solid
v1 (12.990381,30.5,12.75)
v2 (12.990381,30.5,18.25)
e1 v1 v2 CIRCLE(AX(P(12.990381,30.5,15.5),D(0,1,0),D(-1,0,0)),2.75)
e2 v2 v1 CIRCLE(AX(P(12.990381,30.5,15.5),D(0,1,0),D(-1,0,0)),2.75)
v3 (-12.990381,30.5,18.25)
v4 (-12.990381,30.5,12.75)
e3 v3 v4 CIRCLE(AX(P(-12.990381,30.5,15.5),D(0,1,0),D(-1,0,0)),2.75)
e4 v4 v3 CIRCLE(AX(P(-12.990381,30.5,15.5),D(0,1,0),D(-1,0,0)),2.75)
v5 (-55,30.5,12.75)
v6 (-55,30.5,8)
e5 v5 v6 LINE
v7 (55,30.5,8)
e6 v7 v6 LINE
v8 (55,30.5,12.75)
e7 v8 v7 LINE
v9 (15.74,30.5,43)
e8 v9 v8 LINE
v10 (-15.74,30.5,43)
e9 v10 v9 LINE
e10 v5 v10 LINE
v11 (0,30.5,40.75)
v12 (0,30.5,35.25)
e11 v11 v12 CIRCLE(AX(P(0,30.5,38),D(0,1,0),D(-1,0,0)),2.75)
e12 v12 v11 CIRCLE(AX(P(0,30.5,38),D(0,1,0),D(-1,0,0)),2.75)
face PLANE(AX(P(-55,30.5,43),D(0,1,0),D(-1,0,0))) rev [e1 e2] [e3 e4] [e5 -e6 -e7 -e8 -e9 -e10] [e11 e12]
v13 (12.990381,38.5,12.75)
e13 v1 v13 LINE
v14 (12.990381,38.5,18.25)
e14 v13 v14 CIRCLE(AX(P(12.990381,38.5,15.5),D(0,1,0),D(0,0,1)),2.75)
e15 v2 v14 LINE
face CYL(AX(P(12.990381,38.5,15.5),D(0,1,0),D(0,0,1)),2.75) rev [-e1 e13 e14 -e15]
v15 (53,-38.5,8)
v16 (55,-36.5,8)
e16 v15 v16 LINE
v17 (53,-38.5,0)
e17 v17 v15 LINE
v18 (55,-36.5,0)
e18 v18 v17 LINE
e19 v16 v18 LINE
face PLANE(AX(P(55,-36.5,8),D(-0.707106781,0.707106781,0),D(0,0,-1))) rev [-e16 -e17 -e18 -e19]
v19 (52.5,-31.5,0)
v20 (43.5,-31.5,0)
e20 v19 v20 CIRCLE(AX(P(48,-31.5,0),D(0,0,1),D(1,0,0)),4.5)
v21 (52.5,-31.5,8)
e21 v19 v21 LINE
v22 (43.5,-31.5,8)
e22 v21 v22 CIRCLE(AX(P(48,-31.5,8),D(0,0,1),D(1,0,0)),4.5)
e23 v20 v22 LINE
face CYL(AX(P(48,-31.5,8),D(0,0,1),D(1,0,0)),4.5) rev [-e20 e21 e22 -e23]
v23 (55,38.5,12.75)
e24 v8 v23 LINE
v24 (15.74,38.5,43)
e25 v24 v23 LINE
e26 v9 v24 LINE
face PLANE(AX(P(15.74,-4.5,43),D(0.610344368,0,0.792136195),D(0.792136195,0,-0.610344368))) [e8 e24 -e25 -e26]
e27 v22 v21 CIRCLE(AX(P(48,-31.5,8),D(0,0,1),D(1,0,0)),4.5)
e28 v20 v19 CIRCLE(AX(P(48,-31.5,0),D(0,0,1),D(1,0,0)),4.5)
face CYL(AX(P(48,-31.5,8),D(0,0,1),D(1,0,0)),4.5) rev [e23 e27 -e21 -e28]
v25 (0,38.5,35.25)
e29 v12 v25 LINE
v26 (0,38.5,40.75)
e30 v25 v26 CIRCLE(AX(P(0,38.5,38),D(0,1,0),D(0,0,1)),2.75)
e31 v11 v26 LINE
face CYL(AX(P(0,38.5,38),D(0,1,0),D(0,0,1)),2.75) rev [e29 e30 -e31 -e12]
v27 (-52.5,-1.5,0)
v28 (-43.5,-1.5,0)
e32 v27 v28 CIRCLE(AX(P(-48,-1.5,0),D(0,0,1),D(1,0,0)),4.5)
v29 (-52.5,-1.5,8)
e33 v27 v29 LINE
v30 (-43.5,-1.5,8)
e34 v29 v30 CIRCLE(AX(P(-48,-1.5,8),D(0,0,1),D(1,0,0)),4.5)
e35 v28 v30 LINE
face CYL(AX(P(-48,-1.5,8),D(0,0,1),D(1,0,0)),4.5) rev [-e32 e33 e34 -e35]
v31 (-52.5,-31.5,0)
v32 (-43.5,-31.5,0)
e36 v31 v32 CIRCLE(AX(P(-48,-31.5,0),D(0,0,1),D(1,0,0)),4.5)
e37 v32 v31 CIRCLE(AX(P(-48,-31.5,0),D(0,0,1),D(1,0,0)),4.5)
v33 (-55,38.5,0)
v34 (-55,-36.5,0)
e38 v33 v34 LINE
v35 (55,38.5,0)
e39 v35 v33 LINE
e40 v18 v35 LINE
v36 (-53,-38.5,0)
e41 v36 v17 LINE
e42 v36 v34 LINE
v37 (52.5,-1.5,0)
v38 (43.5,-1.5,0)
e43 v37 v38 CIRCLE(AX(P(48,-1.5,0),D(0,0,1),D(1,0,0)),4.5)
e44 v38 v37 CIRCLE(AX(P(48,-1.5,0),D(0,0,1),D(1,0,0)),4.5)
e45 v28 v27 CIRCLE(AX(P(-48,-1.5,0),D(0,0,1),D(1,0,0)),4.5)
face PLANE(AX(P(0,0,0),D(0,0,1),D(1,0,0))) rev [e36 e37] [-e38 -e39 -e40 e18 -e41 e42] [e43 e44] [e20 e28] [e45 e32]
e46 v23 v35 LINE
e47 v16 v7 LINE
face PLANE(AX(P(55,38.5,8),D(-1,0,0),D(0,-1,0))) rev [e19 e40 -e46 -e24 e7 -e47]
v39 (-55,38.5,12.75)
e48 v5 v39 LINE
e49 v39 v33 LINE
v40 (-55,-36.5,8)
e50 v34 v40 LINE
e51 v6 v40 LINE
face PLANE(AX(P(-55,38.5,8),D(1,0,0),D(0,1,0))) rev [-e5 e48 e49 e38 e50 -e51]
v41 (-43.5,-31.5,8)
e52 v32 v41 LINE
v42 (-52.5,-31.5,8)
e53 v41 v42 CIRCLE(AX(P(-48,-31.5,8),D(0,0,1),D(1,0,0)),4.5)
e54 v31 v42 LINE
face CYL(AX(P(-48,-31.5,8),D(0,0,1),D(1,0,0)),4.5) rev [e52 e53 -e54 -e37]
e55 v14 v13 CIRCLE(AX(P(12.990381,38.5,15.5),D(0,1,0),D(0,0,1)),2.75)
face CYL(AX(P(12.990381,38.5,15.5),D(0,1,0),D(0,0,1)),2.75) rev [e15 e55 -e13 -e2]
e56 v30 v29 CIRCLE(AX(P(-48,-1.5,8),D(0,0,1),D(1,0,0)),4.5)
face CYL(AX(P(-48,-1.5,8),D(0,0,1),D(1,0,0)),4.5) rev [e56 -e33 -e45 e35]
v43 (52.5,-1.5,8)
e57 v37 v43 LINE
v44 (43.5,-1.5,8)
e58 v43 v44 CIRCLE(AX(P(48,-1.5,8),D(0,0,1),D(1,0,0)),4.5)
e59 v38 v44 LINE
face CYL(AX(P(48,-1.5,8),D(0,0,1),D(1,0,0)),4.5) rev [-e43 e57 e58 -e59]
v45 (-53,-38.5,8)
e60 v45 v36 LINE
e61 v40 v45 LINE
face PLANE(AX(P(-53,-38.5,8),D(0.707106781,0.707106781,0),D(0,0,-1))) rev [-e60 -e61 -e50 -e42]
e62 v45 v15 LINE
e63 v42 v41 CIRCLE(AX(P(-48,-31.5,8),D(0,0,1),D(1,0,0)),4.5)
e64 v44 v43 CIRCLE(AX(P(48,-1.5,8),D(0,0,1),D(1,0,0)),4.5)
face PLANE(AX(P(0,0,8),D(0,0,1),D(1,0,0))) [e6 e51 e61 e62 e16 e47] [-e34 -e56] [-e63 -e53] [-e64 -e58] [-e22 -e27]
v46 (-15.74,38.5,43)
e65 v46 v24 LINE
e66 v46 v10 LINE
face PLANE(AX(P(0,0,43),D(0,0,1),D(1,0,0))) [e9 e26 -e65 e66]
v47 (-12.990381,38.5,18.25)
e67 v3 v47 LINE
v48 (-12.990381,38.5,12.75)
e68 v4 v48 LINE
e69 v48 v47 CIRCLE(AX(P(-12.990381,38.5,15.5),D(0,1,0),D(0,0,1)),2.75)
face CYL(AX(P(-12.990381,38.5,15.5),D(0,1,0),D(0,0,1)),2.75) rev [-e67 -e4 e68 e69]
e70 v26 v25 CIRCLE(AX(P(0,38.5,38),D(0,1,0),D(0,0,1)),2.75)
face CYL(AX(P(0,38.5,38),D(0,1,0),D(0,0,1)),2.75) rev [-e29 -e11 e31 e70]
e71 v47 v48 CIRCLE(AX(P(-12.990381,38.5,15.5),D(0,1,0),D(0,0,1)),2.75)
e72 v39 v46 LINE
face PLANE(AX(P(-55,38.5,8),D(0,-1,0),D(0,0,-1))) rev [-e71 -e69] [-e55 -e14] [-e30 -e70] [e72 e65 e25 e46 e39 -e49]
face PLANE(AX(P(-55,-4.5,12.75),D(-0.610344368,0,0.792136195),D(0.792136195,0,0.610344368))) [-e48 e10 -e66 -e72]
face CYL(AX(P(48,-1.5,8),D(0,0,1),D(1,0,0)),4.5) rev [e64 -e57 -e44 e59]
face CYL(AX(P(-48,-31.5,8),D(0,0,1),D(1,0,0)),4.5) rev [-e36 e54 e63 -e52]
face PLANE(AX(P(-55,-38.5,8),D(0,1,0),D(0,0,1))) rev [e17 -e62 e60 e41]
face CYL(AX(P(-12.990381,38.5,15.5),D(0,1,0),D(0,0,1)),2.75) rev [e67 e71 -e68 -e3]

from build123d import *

# Parameters (mm, degrees)
SKETCH_1_W              = 110
SKETCH_1_H              = 77
EXTRUDE_1_DEPTH         = 8
SKETCH_2_W              = 110
SKETCH_2_H              = 8
EXTRUDE_3_DEPTH         = 43
SKETCH_4_OUTSIDE_W      = 140.198
SKETCH_4_OUTSIDE_H      = 73.198
CUT_EXTRUDE_1_DEPTH     = 43
HOLE_WIZARD_7_0_7_1_D   = 9
HOLE_WIZARD_5_5_5_5_2_D = 5.5
CHAMFER_1_SIZE          = 2


with BuildPart() as part:
    # 草图1 → 凸台-拉伸1 (new body)
    with BuildSketch(Plane.XY):
        Rectangle(SKETCH_1_W, SKETCH_1_H)
    extrude(amount=EXTRUDE_1_DEPTH)

    # 草图2 → 凸台-拉伸3 (add)
    with BuildSketch(Plane.XY):
        with Locations((0, 34.5)):
            Rectangle(SKETCH_2_W, SKETCH_2_H)
    extrude(amount=EXTRUDE_3_DEPTH)

    # 草图4 outside → 切除-拉伸1 (cut)
    with BuildSketch(Plane(origin=(0, 38.5, 0), x_dir=(1, 0, 0), z_dir=(0, 1, 0))):
        with Locations((0, -21.5)):
            Rectangle(SKETCH_4_OUTSIDE_W, SKETCH_4_OUTSIDE_H)
        Polygon((-55, 0), (55, 0), (55, -12.75), (15.74, -43), (-15.74, -43), (-55, -12.75), align=None, mode=Mode.SUBTRACT)
    extrude(amount=-CUT_EXTRUDE_1_DEPTH, mode=Mode.SUBTRACT)

    # Ø7.0 (7) 直径孔1 (through all)
    with Locations(Plane.XY.offset(8)):
        with Locations((-48, -31.5), (48, -31.5), (48, -1.5), (-48, -1.5)):
            Hole(HOLE_WIZARD_7_0_7_1_D / 2)

    # Ø5.5 (5.5) 直径孔2 (through all)
    with Locations(Plane(origin=(0, 38.5, 0), x_dir=(1, 0, 0), z_dir=(0, 1, 0))):
        with Locations((-12.990381057, -15.5), (12.990381057, -15.5), (0, -38)):
            Hole(HOLE_WIZARD_5_5_5_5_2_D / 2)

    # 倒角1
    chamfer_1_edges = [part.edges().sort_by_distance(p)[0] for p in [
        (55, -38.5, 4),
        (-55, -38.5, 4),
    ]]
    chamfer(chamfer_1_edges, length=CHAMFER_1_SIZE)


solid = part.part
